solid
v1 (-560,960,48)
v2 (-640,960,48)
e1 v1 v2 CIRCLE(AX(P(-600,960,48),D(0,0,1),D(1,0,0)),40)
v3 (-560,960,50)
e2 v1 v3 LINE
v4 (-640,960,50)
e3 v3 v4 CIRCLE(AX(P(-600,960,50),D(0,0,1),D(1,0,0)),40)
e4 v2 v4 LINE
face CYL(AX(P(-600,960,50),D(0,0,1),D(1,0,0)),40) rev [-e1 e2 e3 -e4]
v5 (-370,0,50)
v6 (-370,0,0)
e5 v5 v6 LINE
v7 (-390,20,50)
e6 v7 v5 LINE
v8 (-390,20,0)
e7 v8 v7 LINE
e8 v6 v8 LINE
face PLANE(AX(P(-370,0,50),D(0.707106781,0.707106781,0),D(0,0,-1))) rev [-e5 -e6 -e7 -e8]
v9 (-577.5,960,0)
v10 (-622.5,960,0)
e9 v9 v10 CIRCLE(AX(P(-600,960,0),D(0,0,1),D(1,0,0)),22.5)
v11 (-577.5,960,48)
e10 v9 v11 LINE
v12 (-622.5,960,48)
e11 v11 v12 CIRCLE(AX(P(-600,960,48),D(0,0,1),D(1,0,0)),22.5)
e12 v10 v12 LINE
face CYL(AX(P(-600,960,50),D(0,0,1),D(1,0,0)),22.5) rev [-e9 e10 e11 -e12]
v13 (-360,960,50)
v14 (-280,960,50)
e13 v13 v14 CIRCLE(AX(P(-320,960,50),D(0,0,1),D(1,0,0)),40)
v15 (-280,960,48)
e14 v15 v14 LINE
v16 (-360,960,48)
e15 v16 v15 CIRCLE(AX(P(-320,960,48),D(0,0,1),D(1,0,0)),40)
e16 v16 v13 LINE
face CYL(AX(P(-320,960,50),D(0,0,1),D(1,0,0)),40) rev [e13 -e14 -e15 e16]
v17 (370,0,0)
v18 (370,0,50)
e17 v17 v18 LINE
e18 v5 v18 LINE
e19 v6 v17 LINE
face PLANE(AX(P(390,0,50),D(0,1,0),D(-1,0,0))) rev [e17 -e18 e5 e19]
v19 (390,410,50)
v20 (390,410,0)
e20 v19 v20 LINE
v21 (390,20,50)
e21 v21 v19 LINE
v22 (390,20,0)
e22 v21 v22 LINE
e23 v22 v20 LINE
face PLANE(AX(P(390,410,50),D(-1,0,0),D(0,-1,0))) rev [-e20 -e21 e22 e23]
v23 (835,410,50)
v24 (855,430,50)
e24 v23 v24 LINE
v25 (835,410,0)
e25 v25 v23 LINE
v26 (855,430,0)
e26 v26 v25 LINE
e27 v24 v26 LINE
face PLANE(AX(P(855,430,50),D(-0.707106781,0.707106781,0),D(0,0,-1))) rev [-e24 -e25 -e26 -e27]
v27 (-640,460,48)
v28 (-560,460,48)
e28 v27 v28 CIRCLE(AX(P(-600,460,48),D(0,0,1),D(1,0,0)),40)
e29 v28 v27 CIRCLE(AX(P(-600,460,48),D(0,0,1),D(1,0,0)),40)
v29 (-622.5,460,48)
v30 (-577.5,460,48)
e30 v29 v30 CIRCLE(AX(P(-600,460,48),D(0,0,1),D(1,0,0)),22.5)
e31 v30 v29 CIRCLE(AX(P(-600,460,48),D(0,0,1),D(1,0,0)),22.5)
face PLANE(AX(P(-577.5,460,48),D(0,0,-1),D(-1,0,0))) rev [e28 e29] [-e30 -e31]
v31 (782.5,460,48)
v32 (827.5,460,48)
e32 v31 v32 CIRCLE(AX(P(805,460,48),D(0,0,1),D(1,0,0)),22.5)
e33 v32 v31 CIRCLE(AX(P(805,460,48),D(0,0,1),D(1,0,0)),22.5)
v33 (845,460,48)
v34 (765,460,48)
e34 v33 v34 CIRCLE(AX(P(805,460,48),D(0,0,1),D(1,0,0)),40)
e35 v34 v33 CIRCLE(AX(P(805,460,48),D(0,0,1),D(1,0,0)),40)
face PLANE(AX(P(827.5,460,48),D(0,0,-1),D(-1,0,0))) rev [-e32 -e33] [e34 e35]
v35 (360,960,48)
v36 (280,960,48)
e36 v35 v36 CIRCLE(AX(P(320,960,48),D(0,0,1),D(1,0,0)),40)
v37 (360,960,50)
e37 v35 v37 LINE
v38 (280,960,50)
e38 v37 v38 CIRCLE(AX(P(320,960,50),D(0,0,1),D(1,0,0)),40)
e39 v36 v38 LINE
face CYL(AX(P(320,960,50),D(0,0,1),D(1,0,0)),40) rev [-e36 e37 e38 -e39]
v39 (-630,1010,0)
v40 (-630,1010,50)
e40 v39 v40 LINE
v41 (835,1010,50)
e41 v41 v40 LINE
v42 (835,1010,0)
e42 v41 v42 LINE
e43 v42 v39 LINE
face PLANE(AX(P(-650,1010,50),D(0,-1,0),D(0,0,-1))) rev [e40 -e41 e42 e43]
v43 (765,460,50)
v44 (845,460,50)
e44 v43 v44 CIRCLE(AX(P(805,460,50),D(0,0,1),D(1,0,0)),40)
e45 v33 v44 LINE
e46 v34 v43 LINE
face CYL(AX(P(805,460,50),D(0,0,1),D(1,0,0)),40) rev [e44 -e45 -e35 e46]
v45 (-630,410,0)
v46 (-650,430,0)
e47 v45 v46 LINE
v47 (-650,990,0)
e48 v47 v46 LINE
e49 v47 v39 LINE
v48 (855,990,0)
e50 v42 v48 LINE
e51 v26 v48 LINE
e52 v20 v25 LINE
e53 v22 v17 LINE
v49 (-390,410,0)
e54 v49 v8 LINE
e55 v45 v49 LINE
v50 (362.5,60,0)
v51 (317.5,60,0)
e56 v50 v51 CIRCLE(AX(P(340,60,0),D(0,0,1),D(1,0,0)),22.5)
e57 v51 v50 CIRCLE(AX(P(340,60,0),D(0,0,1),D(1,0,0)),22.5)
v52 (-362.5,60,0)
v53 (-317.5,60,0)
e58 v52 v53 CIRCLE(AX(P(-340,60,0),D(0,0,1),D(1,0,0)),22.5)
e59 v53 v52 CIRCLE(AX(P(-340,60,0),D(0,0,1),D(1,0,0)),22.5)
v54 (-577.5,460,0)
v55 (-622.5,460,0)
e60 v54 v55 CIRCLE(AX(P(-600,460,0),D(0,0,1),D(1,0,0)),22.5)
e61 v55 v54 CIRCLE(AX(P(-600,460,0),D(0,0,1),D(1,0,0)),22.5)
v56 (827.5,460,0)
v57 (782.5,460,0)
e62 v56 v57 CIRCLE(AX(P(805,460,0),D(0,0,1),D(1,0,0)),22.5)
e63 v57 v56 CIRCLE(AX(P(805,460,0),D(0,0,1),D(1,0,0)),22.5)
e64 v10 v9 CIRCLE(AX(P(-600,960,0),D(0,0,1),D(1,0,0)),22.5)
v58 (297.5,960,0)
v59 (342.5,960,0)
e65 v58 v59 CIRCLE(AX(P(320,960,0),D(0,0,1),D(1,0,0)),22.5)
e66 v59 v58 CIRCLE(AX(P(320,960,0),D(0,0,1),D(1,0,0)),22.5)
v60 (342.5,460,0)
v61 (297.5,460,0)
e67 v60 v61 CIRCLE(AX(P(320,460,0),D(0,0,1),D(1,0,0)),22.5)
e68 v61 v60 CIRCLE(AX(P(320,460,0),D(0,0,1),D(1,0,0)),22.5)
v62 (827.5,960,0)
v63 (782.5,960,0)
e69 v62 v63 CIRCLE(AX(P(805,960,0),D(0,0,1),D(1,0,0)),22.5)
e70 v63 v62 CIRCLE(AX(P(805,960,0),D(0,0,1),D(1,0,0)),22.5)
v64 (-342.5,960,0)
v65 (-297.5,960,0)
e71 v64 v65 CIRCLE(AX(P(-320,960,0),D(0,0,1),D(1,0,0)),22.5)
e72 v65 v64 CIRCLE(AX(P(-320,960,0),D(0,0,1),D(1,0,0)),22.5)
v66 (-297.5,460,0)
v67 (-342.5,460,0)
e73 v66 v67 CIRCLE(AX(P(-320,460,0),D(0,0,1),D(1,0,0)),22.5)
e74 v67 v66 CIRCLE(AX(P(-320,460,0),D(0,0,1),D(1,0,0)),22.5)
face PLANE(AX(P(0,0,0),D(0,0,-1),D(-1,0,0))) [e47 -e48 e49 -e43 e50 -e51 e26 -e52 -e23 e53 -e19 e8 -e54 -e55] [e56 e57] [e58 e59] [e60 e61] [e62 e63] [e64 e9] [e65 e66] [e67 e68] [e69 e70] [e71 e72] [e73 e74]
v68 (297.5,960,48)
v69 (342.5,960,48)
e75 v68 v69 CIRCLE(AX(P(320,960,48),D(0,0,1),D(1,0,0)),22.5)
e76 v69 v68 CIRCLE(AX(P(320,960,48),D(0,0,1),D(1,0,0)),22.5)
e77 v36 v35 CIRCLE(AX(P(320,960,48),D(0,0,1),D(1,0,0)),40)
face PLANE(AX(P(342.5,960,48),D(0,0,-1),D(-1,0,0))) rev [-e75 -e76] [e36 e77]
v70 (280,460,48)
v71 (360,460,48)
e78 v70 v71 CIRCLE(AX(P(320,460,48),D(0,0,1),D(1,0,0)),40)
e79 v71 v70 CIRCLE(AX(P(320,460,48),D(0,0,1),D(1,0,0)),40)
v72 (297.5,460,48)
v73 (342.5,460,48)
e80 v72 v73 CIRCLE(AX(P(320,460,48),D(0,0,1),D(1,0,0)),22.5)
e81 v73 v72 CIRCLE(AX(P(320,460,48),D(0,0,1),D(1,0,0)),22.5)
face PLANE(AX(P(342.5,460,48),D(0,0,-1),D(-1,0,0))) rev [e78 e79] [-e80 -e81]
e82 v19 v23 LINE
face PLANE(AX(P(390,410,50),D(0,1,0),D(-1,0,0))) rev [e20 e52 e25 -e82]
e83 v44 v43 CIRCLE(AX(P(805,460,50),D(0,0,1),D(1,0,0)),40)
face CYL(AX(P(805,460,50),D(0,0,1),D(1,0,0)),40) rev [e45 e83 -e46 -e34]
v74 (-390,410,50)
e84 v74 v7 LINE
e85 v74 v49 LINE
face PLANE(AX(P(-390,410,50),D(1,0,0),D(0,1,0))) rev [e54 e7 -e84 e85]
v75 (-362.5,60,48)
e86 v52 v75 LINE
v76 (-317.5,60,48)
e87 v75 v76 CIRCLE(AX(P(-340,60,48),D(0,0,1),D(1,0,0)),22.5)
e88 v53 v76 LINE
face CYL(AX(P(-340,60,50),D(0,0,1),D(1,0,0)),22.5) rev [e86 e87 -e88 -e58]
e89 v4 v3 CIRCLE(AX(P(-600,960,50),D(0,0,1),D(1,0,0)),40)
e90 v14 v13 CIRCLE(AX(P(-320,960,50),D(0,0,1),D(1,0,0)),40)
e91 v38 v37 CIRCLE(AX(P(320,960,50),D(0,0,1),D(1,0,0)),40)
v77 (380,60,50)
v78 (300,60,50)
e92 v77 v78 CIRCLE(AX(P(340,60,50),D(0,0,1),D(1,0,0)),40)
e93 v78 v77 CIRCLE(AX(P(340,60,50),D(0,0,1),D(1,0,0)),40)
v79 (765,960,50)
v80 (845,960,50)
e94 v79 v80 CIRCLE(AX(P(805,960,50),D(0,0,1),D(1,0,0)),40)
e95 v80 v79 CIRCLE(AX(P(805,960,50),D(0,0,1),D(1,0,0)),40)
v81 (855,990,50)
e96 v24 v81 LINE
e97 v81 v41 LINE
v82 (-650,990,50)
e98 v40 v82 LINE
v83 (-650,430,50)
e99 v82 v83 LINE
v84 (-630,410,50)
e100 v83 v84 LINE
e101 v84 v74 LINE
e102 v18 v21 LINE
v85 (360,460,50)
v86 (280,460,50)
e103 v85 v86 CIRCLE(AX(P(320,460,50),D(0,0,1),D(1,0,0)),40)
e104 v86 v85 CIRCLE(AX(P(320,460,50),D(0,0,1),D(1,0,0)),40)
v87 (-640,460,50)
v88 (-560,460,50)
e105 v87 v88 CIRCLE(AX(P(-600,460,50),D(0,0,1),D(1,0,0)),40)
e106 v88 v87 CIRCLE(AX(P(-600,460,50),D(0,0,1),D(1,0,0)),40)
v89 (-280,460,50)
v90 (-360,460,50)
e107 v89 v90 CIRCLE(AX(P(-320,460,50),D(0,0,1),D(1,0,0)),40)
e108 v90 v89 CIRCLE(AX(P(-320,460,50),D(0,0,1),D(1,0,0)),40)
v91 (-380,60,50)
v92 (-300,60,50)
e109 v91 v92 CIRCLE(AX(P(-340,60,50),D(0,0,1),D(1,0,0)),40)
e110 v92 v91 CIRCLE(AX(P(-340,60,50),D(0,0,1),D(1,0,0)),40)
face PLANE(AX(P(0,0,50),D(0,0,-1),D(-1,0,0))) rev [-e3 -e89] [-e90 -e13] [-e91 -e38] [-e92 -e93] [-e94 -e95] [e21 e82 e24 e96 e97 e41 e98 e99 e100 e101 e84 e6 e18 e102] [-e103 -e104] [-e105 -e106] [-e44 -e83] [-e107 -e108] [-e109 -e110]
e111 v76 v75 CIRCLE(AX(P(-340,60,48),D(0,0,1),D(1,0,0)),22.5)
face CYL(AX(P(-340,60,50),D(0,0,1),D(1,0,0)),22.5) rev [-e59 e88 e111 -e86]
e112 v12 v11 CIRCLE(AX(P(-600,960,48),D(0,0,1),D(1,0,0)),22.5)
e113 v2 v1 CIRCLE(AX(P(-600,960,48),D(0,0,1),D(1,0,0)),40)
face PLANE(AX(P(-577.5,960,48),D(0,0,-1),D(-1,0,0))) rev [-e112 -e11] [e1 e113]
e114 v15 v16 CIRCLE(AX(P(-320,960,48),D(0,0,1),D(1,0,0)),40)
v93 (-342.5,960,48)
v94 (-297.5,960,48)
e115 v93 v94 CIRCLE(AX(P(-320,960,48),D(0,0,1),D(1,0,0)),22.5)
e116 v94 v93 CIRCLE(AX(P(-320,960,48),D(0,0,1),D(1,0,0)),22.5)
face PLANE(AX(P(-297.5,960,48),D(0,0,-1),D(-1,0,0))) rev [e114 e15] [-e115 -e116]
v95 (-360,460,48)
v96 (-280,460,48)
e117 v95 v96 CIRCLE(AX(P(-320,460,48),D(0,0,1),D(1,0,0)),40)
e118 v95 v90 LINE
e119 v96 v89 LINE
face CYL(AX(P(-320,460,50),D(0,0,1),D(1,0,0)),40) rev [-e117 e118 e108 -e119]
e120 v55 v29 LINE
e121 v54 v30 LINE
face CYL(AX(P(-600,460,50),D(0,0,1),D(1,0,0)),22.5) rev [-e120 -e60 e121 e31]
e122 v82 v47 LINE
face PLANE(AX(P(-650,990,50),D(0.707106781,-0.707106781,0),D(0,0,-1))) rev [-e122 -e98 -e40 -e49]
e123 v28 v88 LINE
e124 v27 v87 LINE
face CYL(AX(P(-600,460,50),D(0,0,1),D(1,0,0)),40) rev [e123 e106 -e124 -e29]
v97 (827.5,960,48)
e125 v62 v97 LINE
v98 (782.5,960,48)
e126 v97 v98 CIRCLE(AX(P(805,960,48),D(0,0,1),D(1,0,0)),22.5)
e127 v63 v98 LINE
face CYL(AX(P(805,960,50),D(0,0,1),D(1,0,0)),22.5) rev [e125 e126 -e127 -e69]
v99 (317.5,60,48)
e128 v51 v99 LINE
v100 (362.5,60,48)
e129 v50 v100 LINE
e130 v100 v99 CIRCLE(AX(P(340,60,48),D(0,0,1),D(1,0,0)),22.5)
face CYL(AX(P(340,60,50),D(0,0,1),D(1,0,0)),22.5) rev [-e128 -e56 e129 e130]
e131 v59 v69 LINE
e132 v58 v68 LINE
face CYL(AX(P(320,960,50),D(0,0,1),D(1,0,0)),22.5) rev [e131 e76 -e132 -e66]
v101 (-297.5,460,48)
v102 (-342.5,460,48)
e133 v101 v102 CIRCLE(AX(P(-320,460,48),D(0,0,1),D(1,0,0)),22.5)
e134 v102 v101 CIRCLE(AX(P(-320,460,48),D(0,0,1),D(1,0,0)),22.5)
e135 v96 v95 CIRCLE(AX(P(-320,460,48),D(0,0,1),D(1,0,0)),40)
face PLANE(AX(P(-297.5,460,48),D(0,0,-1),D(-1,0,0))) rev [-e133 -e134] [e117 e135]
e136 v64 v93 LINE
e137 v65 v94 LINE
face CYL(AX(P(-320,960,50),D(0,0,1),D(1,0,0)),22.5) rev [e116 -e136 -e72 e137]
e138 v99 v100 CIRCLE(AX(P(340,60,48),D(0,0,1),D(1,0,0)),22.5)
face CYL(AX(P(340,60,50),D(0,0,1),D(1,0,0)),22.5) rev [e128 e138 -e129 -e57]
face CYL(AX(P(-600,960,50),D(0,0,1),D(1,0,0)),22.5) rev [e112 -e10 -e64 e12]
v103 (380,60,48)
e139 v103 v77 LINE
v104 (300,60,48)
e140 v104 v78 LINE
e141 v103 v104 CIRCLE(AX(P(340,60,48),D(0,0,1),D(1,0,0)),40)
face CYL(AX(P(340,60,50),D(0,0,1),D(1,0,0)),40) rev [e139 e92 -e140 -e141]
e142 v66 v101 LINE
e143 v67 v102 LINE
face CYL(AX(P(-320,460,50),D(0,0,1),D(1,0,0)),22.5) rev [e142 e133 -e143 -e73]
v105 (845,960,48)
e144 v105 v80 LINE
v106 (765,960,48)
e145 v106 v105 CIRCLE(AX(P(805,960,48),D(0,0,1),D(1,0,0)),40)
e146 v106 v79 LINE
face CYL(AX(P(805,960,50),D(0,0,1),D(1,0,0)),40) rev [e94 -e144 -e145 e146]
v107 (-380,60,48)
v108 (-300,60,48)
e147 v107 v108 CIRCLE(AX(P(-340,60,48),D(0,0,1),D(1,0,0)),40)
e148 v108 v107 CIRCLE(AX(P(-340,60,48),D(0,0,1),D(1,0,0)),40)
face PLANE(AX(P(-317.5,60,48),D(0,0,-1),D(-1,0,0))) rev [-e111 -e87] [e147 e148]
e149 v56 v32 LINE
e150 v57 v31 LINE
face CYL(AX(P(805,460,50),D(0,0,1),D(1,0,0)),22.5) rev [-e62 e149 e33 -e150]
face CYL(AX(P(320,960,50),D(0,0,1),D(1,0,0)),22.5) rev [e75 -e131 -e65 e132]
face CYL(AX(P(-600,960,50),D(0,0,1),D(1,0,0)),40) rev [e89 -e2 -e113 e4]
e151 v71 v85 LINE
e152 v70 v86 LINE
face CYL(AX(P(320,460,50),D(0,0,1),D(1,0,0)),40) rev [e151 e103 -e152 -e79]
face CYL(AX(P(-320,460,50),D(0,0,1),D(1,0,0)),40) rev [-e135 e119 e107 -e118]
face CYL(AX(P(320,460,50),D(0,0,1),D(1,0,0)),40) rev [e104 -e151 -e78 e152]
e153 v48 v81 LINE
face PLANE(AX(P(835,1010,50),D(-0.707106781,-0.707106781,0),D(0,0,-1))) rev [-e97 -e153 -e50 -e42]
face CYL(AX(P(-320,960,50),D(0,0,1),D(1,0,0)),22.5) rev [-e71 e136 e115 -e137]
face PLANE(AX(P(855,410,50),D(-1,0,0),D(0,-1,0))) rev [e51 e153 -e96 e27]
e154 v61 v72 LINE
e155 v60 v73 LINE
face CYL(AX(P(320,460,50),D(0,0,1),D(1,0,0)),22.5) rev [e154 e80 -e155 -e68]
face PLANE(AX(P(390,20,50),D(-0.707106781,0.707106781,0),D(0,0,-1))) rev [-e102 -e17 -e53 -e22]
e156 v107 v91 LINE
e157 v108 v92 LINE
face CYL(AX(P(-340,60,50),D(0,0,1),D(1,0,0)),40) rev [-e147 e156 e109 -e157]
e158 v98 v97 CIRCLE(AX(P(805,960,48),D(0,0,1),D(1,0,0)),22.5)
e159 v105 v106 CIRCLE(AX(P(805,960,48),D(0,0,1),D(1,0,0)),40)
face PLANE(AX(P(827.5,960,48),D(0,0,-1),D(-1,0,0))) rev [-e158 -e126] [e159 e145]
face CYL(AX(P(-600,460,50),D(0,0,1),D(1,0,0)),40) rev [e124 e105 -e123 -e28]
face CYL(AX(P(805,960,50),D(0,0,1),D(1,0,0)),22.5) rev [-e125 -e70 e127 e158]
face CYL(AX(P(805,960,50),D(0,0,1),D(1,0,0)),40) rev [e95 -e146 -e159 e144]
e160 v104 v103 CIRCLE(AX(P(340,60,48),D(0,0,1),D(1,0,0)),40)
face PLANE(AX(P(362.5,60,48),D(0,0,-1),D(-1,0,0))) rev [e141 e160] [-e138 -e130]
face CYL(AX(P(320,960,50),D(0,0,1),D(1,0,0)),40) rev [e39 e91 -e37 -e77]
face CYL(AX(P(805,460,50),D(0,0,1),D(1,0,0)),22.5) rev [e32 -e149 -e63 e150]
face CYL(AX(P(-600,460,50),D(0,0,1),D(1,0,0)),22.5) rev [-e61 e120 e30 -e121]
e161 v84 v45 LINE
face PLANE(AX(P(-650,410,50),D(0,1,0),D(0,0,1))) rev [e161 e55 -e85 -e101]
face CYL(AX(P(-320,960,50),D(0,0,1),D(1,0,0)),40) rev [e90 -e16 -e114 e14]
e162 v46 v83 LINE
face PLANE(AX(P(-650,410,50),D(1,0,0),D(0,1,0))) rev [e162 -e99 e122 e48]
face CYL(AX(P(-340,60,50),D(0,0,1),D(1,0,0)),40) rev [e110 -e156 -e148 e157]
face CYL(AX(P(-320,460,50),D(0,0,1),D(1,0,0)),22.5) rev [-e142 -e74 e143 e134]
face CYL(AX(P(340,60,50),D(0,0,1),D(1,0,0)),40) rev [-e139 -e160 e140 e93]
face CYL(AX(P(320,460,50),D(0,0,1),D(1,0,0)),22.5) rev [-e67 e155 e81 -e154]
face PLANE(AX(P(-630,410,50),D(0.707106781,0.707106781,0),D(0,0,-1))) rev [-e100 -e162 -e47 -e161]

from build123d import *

# Parameters (mm, degrees)
BOSS_EXTRUDE1_DEPTH = 50
HOLE1_D             = 45
HOLE1_CBORE_D       = 80
HOLE1_CBORE_DEPTH   = 2
CHAMFER1_SIZE       = 20


with BuildPart() as part:
    # Sketch1 → Boss-Extrude1 (new body)
    with BuildSketch(Plane.XY):
        Polygon((390, 410), (855, 410), (855, 1010), (-650, 1010), (-650, 410), (-390, 410), (-390, 0), (390, 0), align=None)
    extrude(amount=BOSS_EXTRUDE1_DEPTH)

    # Hole1 (through all)
    with Locations(Plane.XY.offset(50)):
        with Locations((-600, 960), (320, 960), (805, 960), (-340, 60), (340, 60), (-320, 960), (805, 460), (320, 460), (-320, 460), (-600, 460)):
            CounterBoreHole(HOLE1_D / 2, HOLE1_CBORE_D / 2, HOLE1_CBORE_DEPTH)

    # Chamfer1
    chamfer1_edges = [part.edges().sort_by_distance(p)[0] for p in [
        (-650, 410, 25),
        (-650, 1010, 25),
        (855, 1010, 25),
        (855, 410, 25),
        (390, 0, 25),
        (-390, 0, 25),
    ]]
    chamfer(chamfer1_edges, length=CHAMFER1_SIZE)


solid = part.part
